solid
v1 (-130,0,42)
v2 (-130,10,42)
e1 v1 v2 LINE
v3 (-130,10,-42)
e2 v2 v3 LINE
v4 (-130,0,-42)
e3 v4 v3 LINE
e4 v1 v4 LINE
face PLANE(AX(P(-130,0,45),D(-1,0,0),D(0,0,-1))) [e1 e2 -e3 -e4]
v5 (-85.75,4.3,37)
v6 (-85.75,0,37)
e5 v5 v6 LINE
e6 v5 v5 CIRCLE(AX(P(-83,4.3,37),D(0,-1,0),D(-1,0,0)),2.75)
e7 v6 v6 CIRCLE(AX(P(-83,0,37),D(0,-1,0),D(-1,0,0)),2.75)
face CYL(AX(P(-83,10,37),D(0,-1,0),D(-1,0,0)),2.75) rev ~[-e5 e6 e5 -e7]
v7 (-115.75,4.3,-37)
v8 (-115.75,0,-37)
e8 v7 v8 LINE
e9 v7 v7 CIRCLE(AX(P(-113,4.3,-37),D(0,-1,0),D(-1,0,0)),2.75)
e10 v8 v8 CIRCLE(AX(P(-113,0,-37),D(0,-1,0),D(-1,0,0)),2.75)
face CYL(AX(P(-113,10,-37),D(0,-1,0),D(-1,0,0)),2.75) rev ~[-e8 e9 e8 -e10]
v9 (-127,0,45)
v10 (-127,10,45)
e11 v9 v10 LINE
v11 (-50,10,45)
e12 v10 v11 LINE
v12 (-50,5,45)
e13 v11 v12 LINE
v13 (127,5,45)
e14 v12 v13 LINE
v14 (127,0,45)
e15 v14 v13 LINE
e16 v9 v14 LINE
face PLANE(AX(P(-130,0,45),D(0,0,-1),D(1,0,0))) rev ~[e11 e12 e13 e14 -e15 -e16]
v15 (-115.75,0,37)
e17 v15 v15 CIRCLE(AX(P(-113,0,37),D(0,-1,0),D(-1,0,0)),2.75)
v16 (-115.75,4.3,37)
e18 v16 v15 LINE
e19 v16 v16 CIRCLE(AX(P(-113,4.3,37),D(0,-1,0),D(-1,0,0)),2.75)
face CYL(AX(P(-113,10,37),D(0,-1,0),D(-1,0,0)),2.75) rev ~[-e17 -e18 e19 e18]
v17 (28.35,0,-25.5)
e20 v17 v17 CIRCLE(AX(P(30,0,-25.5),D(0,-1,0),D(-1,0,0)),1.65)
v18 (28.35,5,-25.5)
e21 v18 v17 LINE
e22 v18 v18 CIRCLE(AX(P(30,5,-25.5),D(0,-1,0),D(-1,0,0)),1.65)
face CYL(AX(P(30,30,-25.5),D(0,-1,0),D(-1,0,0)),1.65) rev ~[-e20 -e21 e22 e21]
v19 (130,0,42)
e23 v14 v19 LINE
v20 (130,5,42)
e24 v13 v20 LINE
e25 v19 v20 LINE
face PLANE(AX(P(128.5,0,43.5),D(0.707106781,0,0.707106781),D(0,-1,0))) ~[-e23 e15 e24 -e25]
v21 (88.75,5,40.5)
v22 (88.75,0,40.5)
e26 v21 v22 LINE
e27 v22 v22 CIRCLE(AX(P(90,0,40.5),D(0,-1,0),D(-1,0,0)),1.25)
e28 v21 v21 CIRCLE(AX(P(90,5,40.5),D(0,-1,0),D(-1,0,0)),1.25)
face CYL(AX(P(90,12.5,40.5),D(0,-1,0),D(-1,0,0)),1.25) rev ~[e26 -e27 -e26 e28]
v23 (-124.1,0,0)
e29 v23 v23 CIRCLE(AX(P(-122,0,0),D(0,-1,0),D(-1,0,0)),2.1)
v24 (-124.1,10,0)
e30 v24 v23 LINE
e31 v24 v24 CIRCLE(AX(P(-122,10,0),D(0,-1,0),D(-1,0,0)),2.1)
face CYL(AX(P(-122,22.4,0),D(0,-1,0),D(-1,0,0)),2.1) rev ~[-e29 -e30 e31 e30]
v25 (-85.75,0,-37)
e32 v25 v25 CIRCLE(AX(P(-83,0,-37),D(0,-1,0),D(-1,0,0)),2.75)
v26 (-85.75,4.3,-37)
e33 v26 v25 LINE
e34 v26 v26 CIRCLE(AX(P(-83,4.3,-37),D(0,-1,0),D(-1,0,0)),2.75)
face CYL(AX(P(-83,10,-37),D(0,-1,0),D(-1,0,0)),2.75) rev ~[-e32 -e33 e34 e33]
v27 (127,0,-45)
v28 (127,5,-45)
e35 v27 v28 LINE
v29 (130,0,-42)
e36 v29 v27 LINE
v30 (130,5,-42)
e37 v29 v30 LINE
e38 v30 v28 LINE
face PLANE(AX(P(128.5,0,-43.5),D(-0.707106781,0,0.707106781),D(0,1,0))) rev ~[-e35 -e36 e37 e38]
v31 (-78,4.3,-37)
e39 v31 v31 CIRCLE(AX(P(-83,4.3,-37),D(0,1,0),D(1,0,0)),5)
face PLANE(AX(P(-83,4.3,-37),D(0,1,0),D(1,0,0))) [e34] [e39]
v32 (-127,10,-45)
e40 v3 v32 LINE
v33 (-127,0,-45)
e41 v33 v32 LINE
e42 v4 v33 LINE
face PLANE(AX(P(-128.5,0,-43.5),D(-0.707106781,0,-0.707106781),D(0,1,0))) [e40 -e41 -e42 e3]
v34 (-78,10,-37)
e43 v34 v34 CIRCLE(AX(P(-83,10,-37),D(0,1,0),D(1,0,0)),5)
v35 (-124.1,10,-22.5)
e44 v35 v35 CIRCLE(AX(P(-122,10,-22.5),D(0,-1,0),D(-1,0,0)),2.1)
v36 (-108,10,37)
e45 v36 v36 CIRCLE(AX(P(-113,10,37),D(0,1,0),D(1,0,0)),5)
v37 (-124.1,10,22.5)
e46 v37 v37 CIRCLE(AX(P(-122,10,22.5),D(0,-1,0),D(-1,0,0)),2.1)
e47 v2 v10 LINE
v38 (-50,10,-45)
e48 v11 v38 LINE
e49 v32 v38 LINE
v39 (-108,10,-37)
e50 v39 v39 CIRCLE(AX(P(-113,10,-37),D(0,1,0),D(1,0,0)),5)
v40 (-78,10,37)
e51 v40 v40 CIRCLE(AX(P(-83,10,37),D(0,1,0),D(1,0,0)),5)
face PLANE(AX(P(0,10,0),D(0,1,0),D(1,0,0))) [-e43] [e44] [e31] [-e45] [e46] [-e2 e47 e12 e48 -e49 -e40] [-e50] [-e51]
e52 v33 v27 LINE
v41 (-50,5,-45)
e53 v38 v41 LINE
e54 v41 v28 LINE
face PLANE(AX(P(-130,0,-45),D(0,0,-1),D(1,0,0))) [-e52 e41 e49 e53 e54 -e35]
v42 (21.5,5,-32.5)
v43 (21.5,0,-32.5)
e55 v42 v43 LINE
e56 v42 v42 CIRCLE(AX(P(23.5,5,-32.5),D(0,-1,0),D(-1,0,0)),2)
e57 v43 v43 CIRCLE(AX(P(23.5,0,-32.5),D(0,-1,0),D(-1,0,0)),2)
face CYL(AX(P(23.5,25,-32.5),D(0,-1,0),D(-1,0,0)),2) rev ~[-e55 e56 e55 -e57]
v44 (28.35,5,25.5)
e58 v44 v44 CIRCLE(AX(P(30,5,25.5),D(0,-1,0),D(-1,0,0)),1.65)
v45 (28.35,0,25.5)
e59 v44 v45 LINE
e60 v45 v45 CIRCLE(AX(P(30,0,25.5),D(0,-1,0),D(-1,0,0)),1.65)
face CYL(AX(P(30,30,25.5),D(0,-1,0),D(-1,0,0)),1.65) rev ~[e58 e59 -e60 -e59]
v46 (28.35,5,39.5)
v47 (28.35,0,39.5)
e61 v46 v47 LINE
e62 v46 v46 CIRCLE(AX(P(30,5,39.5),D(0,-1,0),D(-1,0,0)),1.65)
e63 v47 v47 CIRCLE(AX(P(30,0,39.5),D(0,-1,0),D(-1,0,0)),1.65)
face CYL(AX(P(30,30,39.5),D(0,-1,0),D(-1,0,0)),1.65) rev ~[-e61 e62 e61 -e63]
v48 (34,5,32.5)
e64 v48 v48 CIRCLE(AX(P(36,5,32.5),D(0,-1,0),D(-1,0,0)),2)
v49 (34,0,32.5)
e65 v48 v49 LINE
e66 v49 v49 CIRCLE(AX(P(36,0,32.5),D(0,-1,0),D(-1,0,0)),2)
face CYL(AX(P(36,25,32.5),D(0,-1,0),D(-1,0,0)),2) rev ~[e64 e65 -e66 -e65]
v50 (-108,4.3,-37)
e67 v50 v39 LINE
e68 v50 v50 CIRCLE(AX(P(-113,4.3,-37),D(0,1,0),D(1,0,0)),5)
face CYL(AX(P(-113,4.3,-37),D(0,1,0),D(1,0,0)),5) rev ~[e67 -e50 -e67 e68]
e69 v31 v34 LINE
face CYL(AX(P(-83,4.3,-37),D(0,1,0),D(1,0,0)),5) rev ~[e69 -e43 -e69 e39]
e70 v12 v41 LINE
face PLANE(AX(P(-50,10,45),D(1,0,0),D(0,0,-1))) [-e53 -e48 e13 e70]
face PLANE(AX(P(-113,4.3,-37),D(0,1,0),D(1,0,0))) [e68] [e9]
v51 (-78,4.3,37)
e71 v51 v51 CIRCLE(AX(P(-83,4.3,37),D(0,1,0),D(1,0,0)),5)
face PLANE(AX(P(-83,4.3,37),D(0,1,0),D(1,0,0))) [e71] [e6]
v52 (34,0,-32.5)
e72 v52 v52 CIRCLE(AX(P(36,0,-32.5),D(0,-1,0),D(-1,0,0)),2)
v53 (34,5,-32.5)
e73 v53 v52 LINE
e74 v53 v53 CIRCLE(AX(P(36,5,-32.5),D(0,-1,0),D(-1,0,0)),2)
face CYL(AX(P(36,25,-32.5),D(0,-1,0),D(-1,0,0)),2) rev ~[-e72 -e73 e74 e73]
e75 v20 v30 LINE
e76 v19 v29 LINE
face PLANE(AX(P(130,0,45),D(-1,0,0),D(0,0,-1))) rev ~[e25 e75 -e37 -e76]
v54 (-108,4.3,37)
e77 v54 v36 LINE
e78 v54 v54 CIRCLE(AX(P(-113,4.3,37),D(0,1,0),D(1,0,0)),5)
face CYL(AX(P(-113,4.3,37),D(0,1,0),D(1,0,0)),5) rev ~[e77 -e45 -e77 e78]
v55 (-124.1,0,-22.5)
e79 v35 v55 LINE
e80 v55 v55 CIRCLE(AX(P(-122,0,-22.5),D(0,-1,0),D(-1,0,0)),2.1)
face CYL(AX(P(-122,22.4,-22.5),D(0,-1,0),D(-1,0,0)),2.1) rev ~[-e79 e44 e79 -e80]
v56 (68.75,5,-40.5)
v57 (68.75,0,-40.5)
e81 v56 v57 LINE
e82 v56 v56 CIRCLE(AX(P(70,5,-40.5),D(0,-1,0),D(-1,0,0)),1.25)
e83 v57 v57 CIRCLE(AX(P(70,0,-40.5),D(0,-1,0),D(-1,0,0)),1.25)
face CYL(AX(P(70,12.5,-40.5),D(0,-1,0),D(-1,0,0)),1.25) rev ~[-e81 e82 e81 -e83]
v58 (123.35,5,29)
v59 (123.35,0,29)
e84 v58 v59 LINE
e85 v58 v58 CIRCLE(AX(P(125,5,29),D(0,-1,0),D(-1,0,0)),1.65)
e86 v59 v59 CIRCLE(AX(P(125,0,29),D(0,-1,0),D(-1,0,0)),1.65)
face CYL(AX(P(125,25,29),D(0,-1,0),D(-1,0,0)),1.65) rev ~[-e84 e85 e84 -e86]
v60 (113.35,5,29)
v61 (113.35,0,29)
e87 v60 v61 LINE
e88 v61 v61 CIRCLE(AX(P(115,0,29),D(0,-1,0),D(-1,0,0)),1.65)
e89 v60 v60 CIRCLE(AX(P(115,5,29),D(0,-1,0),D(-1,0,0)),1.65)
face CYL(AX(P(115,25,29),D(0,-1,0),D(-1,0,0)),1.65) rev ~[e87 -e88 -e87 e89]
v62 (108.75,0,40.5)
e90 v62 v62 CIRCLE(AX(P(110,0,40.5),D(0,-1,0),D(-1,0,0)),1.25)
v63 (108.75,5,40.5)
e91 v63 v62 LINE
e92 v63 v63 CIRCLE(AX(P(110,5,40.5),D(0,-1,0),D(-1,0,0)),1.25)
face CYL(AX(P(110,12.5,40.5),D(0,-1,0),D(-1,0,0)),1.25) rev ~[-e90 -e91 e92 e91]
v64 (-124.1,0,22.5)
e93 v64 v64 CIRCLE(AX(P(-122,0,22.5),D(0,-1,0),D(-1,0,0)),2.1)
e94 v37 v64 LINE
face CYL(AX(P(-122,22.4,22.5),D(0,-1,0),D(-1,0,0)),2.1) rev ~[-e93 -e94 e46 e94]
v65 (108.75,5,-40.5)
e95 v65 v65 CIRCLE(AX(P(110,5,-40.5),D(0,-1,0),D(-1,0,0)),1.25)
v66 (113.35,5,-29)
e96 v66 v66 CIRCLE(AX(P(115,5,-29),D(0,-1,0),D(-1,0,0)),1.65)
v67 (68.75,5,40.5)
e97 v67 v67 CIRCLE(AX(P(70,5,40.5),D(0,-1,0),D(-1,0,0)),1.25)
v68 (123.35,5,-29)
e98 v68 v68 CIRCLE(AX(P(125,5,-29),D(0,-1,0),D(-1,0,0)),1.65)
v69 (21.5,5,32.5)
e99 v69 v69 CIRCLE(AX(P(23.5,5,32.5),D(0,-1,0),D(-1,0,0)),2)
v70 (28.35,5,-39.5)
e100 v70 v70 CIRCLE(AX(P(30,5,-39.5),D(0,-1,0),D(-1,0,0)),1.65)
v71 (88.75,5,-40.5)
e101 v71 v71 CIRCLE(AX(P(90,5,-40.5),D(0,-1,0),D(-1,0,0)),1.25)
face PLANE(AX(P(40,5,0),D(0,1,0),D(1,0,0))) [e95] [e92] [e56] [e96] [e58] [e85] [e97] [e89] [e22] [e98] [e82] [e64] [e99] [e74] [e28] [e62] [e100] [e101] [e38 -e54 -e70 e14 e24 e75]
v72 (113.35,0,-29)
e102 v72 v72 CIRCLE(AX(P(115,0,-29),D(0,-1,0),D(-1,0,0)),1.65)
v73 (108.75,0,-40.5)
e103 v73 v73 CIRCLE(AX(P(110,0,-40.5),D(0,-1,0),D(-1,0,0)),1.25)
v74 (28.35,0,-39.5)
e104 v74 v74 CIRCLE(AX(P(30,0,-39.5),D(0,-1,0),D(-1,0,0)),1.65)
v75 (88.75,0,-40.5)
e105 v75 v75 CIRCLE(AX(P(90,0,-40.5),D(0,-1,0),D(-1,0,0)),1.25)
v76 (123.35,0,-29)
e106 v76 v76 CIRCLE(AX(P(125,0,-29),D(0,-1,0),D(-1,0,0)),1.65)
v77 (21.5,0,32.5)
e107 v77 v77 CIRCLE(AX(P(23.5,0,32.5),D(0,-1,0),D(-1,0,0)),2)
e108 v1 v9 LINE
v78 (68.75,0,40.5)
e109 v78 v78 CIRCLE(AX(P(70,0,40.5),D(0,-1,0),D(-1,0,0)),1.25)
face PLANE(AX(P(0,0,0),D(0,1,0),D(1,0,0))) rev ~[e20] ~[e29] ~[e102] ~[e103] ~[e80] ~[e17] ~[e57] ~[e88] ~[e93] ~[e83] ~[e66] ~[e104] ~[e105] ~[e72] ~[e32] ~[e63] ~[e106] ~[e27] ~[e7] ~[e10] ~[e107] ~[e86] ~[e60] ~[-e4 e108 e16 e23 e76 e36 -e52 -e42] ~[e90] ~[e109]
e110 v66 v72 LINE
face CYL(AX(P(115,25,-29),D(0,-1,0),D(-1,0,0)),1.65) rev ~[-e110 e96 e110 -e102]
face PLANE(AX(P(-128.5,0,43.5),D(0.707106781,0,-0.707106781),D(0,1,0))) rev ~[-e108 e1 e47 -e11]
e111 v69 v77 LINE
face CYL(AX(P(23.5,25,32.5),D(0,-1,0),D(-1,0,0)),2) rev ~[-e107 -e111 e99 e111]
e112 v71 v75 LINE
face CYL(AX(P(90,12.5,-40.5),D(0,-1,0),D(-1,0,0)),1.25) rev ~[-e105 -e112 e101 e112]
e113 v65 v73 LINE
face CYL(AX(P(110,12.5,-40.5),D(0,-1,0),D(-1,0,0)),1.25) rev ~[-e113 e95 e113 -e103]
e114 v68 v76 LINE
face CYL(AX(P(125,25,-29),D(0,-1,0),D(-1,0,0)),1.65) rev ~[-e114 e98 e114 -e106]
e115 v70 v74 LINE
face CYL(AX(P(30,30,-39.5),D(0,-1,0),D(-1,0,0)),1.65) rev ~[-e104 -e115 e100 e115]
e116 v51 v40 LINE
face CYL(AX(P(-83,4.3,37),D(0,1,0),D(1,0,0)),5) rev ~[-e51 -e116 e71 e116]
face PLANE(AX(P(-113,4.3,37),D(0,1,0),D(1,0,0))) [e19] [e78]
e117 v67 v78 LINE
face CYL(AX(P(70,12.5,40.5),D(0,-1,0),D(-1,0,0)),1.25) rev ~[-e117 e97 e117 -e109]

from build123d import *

# Parameters (mm, degrees)
SKETCH_1_W                = 260
SKETCH_1_H                = 90
EXTRUDE_1_DEPTH           = 10
CHAMFER_1_SIZE            = 3
HOLE_WIZARD_1_D           = 5.5
HOLE_WIZARD_1_DEPTH       = 10.1
HOLE_WIZARD_1_CBORE_D     = 10
HOLE_WIZARD_1_CBORE_DEPTH = 5.7
HOLE_WIZARD_1_TIP         = 1.652366702
HOLE_WIZARD_M5_1_D        = 4.2
HOLE_WIZARD_M5_1_DEPTH    = 12.4
HOLE_WIZARD_M5_1_TIP      = 1.2618073
SKETCH_8_W                = 180
SKETCH_8_H                = 90
CUT_EXTRUDE_1_DEPTH       = 5
HOLE_WIZARD_M3_1_D        = 2.5
HOLE_WIZARD_M3_1_DEPTH    = 7.5
HOLE_WIZARD_M3_1_TIP      = 0.751075774
HOLE_WIZARD_M4_1_D        = 3.3
HOLE_WIZARD_M4_1_DEPTH    = 20
HOLE_WIZARD_M4_1_TIP      = 0.991420021
HOLE_WIZARD_M4_2_D        = 3.3
HOLE_WIZARD_M4_2_DEPTH    = 20
HOLE_WIZARD_M4_2_TIP      = 0.991420021
MM_1_D                    = 4
MM_1_DEPTH                = 20
MM_1_TIP                  = 1.201721238


with BuildPart() as part:
    # 草图1 → 凸台-拉伸1 (new body)
    with BuildSketch(Plane(origin=(0, 0, 0), x_dir=(1, 0, 0), z_dir=(0, 1, 0))):
        Rectangle(SKETCH_1_W, SKETCH_1_H)
    extrude(amount=EXTRUDE_1_DEPTH)

    # 倒角1
    chamfer_1_edges = [part.edges().sort_by_distance(p)[0] for p in [
        (130, 5, 45),
        (-130, 5, 45),
        (-130, 5, -45),
        (130, 5, -45),
    ]]
    chamfer(chamfer_1_edges, length=CHAMFER_1_SIZE)

    # 打孔尺寸(%根据)内六角圆柱头螺钉的类型1
    with Locations(Plane(origin=(0, 10, 0), x_dir=(1, 0, 0), z_dir=(0, 1, 0))):
        with Locations((-83, 37), (-113, 37), (-83, -37), (-113, -37)):
            CounterBoreHole(HOLE_WIZARD_1_D / 2, HOLE_WIZARD_1_CBORE_D / 2, HOLE_WIZARD_1_CBORE_DEPTH, depth=HOLE_WIZARD_1_DEPTH)
            with Locations((0, 0, -(HOLE_WIZARD_1_DEPTH + HOLE_WIZARD_1_TIP / 2))):  # 118° drill point
                Cone(0, HOLE_WIZARD_1_D / 2, HOLE_WIZARD_1_TIP, mode=Mode.SUBTRACT)

    # M5 螺纹孔1
    with Locations(Plane(origin=(0, 10, 0), x_dir=(1, 0, 0), z_dir=(0, 1, 0))):
        with Locations((-122, 22.5), (-122, 0), (-122, -22.5)):
            Hole(HOLE_WIZARD_M5_1_D / 2, depth=HOLE_WIZARD_M5_1_DEPTH)
            with Locations((0, 0, -(HOLE_WIZARD_M5_1_DEPTH + HOLE_WIZARD_M5_1_TIP / 2))):  # 118° drill point
                Cone(0, HOLE_WIZARD_M5_1_D / 2, HOLE_WIZARD_M5_1_TIP, mode=Mode.SUBTRACT)

    # 草图8 → 切除-拉伸1 (cut)
    with BuildSketch(Plane(origin=(0, 10, 0), x_dir=(1, 0, 0), z_dir=(0, 1, 0))):
        with Locations((40, 0)):
            Rectangle(SKETCH_8_W, SKETCH_8_H)
    extrude(amount=-CUT_EXTRUDE_1_DEPTH, mode=Mode.SUBTRACT)

    # M3 螺纹孔1
    with Locations(Plane(origin=(0, 5, 0), x_dir=(1, 0, 0), z_dir=(0, 1, 0))):
        with Locations((110, -40.5), (90, -40.5), (70, -40.5), (110, 40.5), (90, 40.5), (70, 40.5)):
            Hole(HOLE_WIZARD_M3_1_D / 2, depth=HOLE_WIZARD_M3_1_DEPTH)
            with Locations((0, 0, -(HOLE_WIZARD_M3_1_DEPTH + HOLE_WIZARD_M3_1_TIP / 2))):  # 118° drill point
                Cone(0, HOLE_WIZARD_M3_1_D / 2, HOLE_WIZARD_M3_1_TIP, mode=Mode.SUBTRACT)

    # M4 螺纹孔1
    with Locations(Plane(origin=(0, 5, 0), x_dir=(1, 0, 0), z_dir=(0, 1, 0))):
        with Locations((115, -29), (125, -29), (115, 29), (125, 29)):
            Hole(HOLE_WIZARD_M4_1_D / 2, depth=HOLE_WIZARD_M4_1_DEPTH)
            with Locations((0, 0, -(HOLE_WIZARD_M4_1_DEPTH + HOLE_WIZARD_M4_1_TIP / 2))):  # 118° drill point
                Cone(0, HOLE_WIZARD_M4_1_D / 2, HOLE_WIZARD_M4_1_TIP, mode=Mode.SUBTRACT)

    # M4 螺纹孔2
    with Locations(Plane(origin=(0, 10, 0), x_dir=(1, 0, 0), z_dir=(0, 1, 0))):
        with Locations((30, -25.5), (30, -39.5), (30, 25.5), (30, 39.5)):
            Hole(HOLE_WIZARD_M4_2_D / 2, depth=HOLE_WIZARD_M4_2_DEPTH)
            with Locations((0, 0, -(HOLE_WIZARD_M4_2_DEPTH + HOLE_WIZARD_M4_2_TIP / 2))):  # 118° drill point
                Cone(0, HOLE_WIZARD_M4_2_D / 2, HOLE_WIZARD_M4_2_TIP, mode=Mode.SUBTRACT)

    # 大小mm 暗销孔1
    with Locations(Plane(origin=(0, 5, 0), x_dir=(1, 0, 0), z_dir=(0, 1, 0))):
        with Locations((23.5, -32.5), (36, -32.5), (23.5, 32.5), (36, 32.5)):
            Hole(MM_1_D / 2, depth=MM_1_DEPTH)
            with Locations((0, 0, -(MM_1_DEPTH + MM_1_TIP / 2))):  # 118° drill point
                Cone(0, MM_1_D / 2, MM_1_TIP, mode=Mode.SUBTRACT)


solid = part.part
